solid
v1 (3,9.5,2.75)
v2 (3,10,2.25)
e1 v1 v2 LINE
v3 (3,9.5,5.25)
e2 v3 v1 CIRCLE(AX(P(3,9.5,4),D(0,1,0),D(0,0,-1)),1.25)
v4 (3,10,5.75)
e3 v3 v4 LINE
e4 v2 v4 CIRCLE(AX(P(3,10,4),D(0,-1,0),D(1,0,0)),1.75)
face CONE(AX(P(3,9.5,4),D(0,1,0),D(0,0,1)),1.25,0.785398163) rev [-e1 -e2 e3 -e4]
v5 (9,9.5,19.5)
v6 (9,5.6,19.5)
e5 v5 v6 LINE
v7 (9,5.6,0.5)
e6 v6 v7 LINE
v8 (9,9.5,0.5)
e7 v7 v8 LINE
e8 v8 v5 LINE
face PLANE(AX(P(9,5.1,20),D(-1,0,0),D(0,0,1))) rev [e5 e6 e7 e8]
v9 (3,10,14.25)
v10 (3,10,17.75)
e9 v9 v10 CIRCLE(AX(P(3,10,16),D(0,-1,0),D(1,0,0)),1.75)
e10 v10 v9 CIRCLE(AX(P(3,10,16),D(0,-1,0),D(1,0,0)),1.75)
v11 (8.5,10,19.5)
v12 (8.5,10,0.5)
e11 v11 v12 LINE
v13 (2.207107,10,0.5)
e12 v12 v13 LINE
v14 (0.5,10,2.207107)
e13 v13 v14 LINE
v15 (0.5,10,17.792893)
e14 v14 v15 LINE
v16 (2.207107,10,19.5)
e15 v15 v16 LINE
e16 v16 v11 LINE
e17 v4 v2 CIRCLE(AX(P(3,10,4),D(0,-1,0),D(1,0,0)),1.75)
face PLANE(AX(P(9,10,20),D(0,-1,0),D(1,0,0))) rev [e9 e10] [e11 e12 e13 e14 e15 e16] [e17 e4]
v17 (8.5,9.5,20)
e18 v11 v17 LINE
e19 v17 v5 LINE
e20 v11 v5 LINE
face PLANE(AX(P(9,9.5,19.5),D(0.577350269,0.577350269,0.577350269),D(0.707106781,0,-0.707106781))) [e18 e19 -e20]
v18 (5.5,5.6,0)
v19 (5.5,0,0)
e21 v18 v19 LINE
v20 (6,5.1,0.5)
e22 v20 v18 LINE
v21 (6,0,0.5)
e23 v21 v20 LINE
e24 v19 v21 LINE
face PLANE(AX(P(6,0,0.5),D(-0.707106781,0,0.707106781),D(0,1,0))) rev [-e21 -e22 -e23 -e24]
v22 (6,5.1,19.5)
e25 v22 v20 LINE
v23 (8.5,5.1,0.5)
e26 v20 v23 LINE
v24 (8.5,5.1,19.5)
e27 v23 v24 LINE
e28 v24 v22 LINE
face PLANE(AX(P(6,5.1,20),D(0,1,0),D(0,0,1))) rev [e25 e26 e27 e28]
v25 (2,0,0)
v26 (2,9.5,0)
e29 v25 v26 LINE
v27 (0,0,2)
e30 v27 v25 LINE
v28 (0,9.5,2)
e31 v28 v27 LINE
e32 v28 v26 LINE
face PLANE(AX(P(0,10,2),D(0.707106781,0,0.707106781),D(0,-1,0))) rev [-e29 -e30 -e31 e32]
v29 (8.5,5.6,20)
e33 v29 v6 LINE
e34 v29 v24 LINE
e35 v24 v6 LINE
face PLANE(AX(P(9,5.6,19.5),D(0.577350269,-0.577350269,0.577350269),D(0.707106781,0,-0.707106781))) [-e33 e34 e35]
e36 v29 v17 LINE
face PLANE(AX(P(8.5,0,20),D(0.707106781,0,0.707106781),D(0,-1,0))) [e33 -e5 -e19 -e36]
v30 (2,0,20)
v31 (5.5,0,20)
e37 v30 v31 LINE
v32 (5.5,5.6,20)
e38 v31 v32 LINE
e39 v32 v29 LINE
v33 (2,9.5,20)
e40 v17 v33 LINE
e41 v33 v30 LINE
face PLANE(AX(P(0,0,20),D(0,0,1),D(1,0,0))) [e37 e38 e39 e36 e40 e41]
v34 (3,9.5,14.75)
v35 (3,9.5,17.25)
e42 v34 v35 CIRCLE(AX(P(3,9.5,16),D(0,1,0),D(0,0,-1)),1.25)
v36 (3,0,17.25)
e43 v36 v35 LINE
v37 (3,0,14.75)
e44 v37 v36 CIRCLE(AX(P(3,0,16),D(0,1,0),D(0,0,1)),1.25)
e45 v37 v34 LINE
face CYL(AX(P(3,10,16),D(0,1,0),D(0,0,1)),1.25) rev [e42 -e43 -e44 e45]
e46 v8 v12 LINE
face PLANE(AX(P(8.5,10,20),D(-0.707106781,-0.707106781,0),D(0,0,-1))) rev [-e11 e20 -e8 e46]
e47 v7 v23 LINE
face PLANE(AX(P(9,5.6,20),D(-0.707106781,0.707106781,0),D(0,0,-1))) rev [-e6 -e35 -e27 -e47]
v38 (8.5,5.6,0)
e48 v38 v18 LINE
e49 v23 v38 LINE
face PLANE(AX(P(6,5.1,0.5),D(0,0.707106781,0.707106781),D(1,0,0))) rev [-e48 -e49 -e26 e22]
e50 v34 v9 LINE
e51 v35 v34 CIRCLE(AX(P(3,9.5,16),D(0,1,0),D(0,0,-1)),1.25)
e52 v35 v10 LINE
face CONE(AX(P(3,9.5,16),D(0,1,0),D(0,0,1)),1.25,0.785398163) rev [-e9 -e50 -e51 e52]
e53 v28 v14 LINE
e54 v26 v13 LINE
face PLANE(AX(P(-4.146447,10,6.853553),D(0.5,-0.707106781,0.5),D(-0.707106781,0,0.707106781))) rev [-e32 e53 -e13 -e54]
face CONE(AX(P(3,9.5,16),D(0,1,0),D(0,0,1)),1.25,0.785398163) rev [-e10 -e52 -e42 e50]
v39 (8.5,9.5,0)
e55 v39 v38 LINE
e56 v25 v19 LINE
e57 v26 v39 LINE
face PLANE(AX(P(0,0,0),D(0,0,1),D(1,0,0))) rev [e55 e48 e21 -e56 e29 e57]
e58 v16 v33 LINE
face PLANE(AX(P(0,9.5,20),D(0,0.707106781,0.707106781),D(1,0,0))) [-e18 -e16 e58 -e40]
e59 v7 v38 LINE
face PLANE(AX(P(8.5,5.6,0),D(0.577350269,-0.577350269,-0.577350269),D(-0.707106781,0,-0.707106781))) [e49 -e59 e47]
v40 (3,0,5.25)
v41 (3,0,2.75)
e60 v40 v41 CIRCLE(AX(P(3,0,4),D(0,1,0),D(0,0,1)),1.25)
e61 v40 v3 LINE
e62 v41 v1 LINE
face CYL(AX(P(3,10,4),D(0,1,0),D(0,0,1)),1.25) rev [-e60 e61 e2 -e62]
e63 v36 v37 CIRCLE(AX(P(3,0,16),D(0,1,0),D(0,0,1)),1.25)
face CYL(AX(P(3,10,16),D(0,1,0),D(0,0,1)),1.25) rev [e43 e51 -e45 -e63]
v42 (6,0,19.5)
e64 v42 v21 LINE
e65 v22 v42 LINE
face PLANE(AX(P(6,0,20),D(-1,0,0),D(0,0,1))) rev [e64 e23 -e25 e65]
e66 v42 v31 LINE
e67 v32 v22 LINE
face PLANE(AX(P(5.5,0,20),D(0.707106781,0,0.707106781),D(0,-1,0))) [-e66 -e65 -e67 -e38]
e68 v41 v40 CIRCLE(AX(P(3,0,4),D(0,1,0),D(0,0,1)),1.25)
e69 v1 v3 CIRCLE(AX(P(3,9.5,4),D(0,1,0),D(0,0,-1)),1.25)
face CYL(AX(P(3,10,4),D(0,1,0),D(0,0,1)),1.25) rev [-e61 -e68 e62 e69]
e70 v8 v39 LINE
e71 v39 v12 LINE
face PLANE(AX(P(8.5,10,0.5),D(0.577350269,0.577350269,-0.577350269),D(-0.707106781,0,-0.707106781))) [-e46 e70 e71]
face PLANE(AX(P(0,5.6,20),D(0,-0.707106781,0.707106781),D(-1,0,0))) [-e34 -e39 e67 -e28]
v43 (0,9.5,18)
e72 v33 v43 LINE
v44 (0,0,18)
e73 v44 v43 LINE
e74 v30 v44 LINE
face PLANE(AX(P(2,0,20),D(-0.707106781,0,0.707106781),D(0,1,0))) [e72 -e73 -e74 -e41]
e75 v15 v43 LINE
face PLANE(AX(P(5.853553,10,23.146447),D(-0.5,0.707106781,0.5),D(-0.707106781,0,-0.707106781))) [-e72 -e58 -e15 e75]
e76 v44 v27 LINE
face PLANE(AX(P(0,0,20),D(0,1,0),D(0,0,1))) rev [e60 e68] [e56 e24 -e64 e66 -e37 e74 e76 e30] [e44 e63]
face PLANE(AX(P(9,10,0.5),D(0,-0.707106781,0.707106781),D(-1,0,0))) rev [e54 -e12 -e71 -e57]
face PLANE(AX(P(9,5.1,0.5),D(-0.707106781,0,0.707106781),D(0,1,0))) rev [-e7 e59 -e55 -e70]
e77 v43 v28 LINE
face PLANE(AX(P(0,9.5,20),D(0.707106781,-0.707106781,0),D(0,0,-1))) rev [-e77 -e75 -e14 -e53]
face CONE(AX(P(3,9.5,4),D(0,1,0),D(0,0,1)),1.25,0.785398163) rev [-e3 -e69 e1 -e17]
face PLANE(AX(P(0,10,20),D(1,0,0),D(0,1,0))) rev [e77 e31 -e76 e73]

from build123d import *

# Parameters (mm, degrees)
EXTRUDE_1_DEPTH    = 20
HOLE_WIZARD_M3_1_D = 2.5
CHAMFER_1_SIZE     = 2
CHAMFER_2_SIZE     = 0.5


with BuildPart() as part:
    # 草图1 → 凸台-拉伸1 (new body)
    with BuildSketch(Plane.XY):
        Polygon((0, 0), (6, 0), (6, 5.1), (9, 5.1), (9, 10), (0, 10), align=None)
    extrude(amount=EXTRUDE_1_DEPTH)

    # M3 螺纹孔1 (through all)
    with Locations(Plane(origin=(0, 10, 0), x_dir=(1, 0, 0), z_dir=(0, 1, 0))):
        with Locations((3, -16), (3, -4)):
            Hole(HOLE_WIZARD_M3_1_D / 2)

    # 倒角1
    chamfer_1_edges = [part.edges().sort_by_distance(p)[0] for p in [
        (0, 5, 20),
        (0, 5, 0),
    ]]
    chamfer(chamfer_1_edges, length=CHAMFER_1_SIZE)

    # 倒角2
    chamfer_2_edges = [part.edges().sort_by_distance(p)[0] for p in [
        (6, 2.55, 20),
        (9, 10, 10),
        (9, 5.1, 10),
        (7.5, 5.1, 20),
        (0, 10, 10),
        (1, 10, 19),
        (1, 10, 1),
        (9, 7.55, 20),
        (5.5, 10, 20),
        (4.25, 10, 4),
        (4.25, 10, 16),
        (5.5, 10, 0),
        (9, 7.55, 0),
        (7.5, 5.1, 0),
        (6, 2.55, 0),
    ]]
    chamfer(chamfer_2_edges, length=CHAMFER_2_SIZE)


solid = part.part
